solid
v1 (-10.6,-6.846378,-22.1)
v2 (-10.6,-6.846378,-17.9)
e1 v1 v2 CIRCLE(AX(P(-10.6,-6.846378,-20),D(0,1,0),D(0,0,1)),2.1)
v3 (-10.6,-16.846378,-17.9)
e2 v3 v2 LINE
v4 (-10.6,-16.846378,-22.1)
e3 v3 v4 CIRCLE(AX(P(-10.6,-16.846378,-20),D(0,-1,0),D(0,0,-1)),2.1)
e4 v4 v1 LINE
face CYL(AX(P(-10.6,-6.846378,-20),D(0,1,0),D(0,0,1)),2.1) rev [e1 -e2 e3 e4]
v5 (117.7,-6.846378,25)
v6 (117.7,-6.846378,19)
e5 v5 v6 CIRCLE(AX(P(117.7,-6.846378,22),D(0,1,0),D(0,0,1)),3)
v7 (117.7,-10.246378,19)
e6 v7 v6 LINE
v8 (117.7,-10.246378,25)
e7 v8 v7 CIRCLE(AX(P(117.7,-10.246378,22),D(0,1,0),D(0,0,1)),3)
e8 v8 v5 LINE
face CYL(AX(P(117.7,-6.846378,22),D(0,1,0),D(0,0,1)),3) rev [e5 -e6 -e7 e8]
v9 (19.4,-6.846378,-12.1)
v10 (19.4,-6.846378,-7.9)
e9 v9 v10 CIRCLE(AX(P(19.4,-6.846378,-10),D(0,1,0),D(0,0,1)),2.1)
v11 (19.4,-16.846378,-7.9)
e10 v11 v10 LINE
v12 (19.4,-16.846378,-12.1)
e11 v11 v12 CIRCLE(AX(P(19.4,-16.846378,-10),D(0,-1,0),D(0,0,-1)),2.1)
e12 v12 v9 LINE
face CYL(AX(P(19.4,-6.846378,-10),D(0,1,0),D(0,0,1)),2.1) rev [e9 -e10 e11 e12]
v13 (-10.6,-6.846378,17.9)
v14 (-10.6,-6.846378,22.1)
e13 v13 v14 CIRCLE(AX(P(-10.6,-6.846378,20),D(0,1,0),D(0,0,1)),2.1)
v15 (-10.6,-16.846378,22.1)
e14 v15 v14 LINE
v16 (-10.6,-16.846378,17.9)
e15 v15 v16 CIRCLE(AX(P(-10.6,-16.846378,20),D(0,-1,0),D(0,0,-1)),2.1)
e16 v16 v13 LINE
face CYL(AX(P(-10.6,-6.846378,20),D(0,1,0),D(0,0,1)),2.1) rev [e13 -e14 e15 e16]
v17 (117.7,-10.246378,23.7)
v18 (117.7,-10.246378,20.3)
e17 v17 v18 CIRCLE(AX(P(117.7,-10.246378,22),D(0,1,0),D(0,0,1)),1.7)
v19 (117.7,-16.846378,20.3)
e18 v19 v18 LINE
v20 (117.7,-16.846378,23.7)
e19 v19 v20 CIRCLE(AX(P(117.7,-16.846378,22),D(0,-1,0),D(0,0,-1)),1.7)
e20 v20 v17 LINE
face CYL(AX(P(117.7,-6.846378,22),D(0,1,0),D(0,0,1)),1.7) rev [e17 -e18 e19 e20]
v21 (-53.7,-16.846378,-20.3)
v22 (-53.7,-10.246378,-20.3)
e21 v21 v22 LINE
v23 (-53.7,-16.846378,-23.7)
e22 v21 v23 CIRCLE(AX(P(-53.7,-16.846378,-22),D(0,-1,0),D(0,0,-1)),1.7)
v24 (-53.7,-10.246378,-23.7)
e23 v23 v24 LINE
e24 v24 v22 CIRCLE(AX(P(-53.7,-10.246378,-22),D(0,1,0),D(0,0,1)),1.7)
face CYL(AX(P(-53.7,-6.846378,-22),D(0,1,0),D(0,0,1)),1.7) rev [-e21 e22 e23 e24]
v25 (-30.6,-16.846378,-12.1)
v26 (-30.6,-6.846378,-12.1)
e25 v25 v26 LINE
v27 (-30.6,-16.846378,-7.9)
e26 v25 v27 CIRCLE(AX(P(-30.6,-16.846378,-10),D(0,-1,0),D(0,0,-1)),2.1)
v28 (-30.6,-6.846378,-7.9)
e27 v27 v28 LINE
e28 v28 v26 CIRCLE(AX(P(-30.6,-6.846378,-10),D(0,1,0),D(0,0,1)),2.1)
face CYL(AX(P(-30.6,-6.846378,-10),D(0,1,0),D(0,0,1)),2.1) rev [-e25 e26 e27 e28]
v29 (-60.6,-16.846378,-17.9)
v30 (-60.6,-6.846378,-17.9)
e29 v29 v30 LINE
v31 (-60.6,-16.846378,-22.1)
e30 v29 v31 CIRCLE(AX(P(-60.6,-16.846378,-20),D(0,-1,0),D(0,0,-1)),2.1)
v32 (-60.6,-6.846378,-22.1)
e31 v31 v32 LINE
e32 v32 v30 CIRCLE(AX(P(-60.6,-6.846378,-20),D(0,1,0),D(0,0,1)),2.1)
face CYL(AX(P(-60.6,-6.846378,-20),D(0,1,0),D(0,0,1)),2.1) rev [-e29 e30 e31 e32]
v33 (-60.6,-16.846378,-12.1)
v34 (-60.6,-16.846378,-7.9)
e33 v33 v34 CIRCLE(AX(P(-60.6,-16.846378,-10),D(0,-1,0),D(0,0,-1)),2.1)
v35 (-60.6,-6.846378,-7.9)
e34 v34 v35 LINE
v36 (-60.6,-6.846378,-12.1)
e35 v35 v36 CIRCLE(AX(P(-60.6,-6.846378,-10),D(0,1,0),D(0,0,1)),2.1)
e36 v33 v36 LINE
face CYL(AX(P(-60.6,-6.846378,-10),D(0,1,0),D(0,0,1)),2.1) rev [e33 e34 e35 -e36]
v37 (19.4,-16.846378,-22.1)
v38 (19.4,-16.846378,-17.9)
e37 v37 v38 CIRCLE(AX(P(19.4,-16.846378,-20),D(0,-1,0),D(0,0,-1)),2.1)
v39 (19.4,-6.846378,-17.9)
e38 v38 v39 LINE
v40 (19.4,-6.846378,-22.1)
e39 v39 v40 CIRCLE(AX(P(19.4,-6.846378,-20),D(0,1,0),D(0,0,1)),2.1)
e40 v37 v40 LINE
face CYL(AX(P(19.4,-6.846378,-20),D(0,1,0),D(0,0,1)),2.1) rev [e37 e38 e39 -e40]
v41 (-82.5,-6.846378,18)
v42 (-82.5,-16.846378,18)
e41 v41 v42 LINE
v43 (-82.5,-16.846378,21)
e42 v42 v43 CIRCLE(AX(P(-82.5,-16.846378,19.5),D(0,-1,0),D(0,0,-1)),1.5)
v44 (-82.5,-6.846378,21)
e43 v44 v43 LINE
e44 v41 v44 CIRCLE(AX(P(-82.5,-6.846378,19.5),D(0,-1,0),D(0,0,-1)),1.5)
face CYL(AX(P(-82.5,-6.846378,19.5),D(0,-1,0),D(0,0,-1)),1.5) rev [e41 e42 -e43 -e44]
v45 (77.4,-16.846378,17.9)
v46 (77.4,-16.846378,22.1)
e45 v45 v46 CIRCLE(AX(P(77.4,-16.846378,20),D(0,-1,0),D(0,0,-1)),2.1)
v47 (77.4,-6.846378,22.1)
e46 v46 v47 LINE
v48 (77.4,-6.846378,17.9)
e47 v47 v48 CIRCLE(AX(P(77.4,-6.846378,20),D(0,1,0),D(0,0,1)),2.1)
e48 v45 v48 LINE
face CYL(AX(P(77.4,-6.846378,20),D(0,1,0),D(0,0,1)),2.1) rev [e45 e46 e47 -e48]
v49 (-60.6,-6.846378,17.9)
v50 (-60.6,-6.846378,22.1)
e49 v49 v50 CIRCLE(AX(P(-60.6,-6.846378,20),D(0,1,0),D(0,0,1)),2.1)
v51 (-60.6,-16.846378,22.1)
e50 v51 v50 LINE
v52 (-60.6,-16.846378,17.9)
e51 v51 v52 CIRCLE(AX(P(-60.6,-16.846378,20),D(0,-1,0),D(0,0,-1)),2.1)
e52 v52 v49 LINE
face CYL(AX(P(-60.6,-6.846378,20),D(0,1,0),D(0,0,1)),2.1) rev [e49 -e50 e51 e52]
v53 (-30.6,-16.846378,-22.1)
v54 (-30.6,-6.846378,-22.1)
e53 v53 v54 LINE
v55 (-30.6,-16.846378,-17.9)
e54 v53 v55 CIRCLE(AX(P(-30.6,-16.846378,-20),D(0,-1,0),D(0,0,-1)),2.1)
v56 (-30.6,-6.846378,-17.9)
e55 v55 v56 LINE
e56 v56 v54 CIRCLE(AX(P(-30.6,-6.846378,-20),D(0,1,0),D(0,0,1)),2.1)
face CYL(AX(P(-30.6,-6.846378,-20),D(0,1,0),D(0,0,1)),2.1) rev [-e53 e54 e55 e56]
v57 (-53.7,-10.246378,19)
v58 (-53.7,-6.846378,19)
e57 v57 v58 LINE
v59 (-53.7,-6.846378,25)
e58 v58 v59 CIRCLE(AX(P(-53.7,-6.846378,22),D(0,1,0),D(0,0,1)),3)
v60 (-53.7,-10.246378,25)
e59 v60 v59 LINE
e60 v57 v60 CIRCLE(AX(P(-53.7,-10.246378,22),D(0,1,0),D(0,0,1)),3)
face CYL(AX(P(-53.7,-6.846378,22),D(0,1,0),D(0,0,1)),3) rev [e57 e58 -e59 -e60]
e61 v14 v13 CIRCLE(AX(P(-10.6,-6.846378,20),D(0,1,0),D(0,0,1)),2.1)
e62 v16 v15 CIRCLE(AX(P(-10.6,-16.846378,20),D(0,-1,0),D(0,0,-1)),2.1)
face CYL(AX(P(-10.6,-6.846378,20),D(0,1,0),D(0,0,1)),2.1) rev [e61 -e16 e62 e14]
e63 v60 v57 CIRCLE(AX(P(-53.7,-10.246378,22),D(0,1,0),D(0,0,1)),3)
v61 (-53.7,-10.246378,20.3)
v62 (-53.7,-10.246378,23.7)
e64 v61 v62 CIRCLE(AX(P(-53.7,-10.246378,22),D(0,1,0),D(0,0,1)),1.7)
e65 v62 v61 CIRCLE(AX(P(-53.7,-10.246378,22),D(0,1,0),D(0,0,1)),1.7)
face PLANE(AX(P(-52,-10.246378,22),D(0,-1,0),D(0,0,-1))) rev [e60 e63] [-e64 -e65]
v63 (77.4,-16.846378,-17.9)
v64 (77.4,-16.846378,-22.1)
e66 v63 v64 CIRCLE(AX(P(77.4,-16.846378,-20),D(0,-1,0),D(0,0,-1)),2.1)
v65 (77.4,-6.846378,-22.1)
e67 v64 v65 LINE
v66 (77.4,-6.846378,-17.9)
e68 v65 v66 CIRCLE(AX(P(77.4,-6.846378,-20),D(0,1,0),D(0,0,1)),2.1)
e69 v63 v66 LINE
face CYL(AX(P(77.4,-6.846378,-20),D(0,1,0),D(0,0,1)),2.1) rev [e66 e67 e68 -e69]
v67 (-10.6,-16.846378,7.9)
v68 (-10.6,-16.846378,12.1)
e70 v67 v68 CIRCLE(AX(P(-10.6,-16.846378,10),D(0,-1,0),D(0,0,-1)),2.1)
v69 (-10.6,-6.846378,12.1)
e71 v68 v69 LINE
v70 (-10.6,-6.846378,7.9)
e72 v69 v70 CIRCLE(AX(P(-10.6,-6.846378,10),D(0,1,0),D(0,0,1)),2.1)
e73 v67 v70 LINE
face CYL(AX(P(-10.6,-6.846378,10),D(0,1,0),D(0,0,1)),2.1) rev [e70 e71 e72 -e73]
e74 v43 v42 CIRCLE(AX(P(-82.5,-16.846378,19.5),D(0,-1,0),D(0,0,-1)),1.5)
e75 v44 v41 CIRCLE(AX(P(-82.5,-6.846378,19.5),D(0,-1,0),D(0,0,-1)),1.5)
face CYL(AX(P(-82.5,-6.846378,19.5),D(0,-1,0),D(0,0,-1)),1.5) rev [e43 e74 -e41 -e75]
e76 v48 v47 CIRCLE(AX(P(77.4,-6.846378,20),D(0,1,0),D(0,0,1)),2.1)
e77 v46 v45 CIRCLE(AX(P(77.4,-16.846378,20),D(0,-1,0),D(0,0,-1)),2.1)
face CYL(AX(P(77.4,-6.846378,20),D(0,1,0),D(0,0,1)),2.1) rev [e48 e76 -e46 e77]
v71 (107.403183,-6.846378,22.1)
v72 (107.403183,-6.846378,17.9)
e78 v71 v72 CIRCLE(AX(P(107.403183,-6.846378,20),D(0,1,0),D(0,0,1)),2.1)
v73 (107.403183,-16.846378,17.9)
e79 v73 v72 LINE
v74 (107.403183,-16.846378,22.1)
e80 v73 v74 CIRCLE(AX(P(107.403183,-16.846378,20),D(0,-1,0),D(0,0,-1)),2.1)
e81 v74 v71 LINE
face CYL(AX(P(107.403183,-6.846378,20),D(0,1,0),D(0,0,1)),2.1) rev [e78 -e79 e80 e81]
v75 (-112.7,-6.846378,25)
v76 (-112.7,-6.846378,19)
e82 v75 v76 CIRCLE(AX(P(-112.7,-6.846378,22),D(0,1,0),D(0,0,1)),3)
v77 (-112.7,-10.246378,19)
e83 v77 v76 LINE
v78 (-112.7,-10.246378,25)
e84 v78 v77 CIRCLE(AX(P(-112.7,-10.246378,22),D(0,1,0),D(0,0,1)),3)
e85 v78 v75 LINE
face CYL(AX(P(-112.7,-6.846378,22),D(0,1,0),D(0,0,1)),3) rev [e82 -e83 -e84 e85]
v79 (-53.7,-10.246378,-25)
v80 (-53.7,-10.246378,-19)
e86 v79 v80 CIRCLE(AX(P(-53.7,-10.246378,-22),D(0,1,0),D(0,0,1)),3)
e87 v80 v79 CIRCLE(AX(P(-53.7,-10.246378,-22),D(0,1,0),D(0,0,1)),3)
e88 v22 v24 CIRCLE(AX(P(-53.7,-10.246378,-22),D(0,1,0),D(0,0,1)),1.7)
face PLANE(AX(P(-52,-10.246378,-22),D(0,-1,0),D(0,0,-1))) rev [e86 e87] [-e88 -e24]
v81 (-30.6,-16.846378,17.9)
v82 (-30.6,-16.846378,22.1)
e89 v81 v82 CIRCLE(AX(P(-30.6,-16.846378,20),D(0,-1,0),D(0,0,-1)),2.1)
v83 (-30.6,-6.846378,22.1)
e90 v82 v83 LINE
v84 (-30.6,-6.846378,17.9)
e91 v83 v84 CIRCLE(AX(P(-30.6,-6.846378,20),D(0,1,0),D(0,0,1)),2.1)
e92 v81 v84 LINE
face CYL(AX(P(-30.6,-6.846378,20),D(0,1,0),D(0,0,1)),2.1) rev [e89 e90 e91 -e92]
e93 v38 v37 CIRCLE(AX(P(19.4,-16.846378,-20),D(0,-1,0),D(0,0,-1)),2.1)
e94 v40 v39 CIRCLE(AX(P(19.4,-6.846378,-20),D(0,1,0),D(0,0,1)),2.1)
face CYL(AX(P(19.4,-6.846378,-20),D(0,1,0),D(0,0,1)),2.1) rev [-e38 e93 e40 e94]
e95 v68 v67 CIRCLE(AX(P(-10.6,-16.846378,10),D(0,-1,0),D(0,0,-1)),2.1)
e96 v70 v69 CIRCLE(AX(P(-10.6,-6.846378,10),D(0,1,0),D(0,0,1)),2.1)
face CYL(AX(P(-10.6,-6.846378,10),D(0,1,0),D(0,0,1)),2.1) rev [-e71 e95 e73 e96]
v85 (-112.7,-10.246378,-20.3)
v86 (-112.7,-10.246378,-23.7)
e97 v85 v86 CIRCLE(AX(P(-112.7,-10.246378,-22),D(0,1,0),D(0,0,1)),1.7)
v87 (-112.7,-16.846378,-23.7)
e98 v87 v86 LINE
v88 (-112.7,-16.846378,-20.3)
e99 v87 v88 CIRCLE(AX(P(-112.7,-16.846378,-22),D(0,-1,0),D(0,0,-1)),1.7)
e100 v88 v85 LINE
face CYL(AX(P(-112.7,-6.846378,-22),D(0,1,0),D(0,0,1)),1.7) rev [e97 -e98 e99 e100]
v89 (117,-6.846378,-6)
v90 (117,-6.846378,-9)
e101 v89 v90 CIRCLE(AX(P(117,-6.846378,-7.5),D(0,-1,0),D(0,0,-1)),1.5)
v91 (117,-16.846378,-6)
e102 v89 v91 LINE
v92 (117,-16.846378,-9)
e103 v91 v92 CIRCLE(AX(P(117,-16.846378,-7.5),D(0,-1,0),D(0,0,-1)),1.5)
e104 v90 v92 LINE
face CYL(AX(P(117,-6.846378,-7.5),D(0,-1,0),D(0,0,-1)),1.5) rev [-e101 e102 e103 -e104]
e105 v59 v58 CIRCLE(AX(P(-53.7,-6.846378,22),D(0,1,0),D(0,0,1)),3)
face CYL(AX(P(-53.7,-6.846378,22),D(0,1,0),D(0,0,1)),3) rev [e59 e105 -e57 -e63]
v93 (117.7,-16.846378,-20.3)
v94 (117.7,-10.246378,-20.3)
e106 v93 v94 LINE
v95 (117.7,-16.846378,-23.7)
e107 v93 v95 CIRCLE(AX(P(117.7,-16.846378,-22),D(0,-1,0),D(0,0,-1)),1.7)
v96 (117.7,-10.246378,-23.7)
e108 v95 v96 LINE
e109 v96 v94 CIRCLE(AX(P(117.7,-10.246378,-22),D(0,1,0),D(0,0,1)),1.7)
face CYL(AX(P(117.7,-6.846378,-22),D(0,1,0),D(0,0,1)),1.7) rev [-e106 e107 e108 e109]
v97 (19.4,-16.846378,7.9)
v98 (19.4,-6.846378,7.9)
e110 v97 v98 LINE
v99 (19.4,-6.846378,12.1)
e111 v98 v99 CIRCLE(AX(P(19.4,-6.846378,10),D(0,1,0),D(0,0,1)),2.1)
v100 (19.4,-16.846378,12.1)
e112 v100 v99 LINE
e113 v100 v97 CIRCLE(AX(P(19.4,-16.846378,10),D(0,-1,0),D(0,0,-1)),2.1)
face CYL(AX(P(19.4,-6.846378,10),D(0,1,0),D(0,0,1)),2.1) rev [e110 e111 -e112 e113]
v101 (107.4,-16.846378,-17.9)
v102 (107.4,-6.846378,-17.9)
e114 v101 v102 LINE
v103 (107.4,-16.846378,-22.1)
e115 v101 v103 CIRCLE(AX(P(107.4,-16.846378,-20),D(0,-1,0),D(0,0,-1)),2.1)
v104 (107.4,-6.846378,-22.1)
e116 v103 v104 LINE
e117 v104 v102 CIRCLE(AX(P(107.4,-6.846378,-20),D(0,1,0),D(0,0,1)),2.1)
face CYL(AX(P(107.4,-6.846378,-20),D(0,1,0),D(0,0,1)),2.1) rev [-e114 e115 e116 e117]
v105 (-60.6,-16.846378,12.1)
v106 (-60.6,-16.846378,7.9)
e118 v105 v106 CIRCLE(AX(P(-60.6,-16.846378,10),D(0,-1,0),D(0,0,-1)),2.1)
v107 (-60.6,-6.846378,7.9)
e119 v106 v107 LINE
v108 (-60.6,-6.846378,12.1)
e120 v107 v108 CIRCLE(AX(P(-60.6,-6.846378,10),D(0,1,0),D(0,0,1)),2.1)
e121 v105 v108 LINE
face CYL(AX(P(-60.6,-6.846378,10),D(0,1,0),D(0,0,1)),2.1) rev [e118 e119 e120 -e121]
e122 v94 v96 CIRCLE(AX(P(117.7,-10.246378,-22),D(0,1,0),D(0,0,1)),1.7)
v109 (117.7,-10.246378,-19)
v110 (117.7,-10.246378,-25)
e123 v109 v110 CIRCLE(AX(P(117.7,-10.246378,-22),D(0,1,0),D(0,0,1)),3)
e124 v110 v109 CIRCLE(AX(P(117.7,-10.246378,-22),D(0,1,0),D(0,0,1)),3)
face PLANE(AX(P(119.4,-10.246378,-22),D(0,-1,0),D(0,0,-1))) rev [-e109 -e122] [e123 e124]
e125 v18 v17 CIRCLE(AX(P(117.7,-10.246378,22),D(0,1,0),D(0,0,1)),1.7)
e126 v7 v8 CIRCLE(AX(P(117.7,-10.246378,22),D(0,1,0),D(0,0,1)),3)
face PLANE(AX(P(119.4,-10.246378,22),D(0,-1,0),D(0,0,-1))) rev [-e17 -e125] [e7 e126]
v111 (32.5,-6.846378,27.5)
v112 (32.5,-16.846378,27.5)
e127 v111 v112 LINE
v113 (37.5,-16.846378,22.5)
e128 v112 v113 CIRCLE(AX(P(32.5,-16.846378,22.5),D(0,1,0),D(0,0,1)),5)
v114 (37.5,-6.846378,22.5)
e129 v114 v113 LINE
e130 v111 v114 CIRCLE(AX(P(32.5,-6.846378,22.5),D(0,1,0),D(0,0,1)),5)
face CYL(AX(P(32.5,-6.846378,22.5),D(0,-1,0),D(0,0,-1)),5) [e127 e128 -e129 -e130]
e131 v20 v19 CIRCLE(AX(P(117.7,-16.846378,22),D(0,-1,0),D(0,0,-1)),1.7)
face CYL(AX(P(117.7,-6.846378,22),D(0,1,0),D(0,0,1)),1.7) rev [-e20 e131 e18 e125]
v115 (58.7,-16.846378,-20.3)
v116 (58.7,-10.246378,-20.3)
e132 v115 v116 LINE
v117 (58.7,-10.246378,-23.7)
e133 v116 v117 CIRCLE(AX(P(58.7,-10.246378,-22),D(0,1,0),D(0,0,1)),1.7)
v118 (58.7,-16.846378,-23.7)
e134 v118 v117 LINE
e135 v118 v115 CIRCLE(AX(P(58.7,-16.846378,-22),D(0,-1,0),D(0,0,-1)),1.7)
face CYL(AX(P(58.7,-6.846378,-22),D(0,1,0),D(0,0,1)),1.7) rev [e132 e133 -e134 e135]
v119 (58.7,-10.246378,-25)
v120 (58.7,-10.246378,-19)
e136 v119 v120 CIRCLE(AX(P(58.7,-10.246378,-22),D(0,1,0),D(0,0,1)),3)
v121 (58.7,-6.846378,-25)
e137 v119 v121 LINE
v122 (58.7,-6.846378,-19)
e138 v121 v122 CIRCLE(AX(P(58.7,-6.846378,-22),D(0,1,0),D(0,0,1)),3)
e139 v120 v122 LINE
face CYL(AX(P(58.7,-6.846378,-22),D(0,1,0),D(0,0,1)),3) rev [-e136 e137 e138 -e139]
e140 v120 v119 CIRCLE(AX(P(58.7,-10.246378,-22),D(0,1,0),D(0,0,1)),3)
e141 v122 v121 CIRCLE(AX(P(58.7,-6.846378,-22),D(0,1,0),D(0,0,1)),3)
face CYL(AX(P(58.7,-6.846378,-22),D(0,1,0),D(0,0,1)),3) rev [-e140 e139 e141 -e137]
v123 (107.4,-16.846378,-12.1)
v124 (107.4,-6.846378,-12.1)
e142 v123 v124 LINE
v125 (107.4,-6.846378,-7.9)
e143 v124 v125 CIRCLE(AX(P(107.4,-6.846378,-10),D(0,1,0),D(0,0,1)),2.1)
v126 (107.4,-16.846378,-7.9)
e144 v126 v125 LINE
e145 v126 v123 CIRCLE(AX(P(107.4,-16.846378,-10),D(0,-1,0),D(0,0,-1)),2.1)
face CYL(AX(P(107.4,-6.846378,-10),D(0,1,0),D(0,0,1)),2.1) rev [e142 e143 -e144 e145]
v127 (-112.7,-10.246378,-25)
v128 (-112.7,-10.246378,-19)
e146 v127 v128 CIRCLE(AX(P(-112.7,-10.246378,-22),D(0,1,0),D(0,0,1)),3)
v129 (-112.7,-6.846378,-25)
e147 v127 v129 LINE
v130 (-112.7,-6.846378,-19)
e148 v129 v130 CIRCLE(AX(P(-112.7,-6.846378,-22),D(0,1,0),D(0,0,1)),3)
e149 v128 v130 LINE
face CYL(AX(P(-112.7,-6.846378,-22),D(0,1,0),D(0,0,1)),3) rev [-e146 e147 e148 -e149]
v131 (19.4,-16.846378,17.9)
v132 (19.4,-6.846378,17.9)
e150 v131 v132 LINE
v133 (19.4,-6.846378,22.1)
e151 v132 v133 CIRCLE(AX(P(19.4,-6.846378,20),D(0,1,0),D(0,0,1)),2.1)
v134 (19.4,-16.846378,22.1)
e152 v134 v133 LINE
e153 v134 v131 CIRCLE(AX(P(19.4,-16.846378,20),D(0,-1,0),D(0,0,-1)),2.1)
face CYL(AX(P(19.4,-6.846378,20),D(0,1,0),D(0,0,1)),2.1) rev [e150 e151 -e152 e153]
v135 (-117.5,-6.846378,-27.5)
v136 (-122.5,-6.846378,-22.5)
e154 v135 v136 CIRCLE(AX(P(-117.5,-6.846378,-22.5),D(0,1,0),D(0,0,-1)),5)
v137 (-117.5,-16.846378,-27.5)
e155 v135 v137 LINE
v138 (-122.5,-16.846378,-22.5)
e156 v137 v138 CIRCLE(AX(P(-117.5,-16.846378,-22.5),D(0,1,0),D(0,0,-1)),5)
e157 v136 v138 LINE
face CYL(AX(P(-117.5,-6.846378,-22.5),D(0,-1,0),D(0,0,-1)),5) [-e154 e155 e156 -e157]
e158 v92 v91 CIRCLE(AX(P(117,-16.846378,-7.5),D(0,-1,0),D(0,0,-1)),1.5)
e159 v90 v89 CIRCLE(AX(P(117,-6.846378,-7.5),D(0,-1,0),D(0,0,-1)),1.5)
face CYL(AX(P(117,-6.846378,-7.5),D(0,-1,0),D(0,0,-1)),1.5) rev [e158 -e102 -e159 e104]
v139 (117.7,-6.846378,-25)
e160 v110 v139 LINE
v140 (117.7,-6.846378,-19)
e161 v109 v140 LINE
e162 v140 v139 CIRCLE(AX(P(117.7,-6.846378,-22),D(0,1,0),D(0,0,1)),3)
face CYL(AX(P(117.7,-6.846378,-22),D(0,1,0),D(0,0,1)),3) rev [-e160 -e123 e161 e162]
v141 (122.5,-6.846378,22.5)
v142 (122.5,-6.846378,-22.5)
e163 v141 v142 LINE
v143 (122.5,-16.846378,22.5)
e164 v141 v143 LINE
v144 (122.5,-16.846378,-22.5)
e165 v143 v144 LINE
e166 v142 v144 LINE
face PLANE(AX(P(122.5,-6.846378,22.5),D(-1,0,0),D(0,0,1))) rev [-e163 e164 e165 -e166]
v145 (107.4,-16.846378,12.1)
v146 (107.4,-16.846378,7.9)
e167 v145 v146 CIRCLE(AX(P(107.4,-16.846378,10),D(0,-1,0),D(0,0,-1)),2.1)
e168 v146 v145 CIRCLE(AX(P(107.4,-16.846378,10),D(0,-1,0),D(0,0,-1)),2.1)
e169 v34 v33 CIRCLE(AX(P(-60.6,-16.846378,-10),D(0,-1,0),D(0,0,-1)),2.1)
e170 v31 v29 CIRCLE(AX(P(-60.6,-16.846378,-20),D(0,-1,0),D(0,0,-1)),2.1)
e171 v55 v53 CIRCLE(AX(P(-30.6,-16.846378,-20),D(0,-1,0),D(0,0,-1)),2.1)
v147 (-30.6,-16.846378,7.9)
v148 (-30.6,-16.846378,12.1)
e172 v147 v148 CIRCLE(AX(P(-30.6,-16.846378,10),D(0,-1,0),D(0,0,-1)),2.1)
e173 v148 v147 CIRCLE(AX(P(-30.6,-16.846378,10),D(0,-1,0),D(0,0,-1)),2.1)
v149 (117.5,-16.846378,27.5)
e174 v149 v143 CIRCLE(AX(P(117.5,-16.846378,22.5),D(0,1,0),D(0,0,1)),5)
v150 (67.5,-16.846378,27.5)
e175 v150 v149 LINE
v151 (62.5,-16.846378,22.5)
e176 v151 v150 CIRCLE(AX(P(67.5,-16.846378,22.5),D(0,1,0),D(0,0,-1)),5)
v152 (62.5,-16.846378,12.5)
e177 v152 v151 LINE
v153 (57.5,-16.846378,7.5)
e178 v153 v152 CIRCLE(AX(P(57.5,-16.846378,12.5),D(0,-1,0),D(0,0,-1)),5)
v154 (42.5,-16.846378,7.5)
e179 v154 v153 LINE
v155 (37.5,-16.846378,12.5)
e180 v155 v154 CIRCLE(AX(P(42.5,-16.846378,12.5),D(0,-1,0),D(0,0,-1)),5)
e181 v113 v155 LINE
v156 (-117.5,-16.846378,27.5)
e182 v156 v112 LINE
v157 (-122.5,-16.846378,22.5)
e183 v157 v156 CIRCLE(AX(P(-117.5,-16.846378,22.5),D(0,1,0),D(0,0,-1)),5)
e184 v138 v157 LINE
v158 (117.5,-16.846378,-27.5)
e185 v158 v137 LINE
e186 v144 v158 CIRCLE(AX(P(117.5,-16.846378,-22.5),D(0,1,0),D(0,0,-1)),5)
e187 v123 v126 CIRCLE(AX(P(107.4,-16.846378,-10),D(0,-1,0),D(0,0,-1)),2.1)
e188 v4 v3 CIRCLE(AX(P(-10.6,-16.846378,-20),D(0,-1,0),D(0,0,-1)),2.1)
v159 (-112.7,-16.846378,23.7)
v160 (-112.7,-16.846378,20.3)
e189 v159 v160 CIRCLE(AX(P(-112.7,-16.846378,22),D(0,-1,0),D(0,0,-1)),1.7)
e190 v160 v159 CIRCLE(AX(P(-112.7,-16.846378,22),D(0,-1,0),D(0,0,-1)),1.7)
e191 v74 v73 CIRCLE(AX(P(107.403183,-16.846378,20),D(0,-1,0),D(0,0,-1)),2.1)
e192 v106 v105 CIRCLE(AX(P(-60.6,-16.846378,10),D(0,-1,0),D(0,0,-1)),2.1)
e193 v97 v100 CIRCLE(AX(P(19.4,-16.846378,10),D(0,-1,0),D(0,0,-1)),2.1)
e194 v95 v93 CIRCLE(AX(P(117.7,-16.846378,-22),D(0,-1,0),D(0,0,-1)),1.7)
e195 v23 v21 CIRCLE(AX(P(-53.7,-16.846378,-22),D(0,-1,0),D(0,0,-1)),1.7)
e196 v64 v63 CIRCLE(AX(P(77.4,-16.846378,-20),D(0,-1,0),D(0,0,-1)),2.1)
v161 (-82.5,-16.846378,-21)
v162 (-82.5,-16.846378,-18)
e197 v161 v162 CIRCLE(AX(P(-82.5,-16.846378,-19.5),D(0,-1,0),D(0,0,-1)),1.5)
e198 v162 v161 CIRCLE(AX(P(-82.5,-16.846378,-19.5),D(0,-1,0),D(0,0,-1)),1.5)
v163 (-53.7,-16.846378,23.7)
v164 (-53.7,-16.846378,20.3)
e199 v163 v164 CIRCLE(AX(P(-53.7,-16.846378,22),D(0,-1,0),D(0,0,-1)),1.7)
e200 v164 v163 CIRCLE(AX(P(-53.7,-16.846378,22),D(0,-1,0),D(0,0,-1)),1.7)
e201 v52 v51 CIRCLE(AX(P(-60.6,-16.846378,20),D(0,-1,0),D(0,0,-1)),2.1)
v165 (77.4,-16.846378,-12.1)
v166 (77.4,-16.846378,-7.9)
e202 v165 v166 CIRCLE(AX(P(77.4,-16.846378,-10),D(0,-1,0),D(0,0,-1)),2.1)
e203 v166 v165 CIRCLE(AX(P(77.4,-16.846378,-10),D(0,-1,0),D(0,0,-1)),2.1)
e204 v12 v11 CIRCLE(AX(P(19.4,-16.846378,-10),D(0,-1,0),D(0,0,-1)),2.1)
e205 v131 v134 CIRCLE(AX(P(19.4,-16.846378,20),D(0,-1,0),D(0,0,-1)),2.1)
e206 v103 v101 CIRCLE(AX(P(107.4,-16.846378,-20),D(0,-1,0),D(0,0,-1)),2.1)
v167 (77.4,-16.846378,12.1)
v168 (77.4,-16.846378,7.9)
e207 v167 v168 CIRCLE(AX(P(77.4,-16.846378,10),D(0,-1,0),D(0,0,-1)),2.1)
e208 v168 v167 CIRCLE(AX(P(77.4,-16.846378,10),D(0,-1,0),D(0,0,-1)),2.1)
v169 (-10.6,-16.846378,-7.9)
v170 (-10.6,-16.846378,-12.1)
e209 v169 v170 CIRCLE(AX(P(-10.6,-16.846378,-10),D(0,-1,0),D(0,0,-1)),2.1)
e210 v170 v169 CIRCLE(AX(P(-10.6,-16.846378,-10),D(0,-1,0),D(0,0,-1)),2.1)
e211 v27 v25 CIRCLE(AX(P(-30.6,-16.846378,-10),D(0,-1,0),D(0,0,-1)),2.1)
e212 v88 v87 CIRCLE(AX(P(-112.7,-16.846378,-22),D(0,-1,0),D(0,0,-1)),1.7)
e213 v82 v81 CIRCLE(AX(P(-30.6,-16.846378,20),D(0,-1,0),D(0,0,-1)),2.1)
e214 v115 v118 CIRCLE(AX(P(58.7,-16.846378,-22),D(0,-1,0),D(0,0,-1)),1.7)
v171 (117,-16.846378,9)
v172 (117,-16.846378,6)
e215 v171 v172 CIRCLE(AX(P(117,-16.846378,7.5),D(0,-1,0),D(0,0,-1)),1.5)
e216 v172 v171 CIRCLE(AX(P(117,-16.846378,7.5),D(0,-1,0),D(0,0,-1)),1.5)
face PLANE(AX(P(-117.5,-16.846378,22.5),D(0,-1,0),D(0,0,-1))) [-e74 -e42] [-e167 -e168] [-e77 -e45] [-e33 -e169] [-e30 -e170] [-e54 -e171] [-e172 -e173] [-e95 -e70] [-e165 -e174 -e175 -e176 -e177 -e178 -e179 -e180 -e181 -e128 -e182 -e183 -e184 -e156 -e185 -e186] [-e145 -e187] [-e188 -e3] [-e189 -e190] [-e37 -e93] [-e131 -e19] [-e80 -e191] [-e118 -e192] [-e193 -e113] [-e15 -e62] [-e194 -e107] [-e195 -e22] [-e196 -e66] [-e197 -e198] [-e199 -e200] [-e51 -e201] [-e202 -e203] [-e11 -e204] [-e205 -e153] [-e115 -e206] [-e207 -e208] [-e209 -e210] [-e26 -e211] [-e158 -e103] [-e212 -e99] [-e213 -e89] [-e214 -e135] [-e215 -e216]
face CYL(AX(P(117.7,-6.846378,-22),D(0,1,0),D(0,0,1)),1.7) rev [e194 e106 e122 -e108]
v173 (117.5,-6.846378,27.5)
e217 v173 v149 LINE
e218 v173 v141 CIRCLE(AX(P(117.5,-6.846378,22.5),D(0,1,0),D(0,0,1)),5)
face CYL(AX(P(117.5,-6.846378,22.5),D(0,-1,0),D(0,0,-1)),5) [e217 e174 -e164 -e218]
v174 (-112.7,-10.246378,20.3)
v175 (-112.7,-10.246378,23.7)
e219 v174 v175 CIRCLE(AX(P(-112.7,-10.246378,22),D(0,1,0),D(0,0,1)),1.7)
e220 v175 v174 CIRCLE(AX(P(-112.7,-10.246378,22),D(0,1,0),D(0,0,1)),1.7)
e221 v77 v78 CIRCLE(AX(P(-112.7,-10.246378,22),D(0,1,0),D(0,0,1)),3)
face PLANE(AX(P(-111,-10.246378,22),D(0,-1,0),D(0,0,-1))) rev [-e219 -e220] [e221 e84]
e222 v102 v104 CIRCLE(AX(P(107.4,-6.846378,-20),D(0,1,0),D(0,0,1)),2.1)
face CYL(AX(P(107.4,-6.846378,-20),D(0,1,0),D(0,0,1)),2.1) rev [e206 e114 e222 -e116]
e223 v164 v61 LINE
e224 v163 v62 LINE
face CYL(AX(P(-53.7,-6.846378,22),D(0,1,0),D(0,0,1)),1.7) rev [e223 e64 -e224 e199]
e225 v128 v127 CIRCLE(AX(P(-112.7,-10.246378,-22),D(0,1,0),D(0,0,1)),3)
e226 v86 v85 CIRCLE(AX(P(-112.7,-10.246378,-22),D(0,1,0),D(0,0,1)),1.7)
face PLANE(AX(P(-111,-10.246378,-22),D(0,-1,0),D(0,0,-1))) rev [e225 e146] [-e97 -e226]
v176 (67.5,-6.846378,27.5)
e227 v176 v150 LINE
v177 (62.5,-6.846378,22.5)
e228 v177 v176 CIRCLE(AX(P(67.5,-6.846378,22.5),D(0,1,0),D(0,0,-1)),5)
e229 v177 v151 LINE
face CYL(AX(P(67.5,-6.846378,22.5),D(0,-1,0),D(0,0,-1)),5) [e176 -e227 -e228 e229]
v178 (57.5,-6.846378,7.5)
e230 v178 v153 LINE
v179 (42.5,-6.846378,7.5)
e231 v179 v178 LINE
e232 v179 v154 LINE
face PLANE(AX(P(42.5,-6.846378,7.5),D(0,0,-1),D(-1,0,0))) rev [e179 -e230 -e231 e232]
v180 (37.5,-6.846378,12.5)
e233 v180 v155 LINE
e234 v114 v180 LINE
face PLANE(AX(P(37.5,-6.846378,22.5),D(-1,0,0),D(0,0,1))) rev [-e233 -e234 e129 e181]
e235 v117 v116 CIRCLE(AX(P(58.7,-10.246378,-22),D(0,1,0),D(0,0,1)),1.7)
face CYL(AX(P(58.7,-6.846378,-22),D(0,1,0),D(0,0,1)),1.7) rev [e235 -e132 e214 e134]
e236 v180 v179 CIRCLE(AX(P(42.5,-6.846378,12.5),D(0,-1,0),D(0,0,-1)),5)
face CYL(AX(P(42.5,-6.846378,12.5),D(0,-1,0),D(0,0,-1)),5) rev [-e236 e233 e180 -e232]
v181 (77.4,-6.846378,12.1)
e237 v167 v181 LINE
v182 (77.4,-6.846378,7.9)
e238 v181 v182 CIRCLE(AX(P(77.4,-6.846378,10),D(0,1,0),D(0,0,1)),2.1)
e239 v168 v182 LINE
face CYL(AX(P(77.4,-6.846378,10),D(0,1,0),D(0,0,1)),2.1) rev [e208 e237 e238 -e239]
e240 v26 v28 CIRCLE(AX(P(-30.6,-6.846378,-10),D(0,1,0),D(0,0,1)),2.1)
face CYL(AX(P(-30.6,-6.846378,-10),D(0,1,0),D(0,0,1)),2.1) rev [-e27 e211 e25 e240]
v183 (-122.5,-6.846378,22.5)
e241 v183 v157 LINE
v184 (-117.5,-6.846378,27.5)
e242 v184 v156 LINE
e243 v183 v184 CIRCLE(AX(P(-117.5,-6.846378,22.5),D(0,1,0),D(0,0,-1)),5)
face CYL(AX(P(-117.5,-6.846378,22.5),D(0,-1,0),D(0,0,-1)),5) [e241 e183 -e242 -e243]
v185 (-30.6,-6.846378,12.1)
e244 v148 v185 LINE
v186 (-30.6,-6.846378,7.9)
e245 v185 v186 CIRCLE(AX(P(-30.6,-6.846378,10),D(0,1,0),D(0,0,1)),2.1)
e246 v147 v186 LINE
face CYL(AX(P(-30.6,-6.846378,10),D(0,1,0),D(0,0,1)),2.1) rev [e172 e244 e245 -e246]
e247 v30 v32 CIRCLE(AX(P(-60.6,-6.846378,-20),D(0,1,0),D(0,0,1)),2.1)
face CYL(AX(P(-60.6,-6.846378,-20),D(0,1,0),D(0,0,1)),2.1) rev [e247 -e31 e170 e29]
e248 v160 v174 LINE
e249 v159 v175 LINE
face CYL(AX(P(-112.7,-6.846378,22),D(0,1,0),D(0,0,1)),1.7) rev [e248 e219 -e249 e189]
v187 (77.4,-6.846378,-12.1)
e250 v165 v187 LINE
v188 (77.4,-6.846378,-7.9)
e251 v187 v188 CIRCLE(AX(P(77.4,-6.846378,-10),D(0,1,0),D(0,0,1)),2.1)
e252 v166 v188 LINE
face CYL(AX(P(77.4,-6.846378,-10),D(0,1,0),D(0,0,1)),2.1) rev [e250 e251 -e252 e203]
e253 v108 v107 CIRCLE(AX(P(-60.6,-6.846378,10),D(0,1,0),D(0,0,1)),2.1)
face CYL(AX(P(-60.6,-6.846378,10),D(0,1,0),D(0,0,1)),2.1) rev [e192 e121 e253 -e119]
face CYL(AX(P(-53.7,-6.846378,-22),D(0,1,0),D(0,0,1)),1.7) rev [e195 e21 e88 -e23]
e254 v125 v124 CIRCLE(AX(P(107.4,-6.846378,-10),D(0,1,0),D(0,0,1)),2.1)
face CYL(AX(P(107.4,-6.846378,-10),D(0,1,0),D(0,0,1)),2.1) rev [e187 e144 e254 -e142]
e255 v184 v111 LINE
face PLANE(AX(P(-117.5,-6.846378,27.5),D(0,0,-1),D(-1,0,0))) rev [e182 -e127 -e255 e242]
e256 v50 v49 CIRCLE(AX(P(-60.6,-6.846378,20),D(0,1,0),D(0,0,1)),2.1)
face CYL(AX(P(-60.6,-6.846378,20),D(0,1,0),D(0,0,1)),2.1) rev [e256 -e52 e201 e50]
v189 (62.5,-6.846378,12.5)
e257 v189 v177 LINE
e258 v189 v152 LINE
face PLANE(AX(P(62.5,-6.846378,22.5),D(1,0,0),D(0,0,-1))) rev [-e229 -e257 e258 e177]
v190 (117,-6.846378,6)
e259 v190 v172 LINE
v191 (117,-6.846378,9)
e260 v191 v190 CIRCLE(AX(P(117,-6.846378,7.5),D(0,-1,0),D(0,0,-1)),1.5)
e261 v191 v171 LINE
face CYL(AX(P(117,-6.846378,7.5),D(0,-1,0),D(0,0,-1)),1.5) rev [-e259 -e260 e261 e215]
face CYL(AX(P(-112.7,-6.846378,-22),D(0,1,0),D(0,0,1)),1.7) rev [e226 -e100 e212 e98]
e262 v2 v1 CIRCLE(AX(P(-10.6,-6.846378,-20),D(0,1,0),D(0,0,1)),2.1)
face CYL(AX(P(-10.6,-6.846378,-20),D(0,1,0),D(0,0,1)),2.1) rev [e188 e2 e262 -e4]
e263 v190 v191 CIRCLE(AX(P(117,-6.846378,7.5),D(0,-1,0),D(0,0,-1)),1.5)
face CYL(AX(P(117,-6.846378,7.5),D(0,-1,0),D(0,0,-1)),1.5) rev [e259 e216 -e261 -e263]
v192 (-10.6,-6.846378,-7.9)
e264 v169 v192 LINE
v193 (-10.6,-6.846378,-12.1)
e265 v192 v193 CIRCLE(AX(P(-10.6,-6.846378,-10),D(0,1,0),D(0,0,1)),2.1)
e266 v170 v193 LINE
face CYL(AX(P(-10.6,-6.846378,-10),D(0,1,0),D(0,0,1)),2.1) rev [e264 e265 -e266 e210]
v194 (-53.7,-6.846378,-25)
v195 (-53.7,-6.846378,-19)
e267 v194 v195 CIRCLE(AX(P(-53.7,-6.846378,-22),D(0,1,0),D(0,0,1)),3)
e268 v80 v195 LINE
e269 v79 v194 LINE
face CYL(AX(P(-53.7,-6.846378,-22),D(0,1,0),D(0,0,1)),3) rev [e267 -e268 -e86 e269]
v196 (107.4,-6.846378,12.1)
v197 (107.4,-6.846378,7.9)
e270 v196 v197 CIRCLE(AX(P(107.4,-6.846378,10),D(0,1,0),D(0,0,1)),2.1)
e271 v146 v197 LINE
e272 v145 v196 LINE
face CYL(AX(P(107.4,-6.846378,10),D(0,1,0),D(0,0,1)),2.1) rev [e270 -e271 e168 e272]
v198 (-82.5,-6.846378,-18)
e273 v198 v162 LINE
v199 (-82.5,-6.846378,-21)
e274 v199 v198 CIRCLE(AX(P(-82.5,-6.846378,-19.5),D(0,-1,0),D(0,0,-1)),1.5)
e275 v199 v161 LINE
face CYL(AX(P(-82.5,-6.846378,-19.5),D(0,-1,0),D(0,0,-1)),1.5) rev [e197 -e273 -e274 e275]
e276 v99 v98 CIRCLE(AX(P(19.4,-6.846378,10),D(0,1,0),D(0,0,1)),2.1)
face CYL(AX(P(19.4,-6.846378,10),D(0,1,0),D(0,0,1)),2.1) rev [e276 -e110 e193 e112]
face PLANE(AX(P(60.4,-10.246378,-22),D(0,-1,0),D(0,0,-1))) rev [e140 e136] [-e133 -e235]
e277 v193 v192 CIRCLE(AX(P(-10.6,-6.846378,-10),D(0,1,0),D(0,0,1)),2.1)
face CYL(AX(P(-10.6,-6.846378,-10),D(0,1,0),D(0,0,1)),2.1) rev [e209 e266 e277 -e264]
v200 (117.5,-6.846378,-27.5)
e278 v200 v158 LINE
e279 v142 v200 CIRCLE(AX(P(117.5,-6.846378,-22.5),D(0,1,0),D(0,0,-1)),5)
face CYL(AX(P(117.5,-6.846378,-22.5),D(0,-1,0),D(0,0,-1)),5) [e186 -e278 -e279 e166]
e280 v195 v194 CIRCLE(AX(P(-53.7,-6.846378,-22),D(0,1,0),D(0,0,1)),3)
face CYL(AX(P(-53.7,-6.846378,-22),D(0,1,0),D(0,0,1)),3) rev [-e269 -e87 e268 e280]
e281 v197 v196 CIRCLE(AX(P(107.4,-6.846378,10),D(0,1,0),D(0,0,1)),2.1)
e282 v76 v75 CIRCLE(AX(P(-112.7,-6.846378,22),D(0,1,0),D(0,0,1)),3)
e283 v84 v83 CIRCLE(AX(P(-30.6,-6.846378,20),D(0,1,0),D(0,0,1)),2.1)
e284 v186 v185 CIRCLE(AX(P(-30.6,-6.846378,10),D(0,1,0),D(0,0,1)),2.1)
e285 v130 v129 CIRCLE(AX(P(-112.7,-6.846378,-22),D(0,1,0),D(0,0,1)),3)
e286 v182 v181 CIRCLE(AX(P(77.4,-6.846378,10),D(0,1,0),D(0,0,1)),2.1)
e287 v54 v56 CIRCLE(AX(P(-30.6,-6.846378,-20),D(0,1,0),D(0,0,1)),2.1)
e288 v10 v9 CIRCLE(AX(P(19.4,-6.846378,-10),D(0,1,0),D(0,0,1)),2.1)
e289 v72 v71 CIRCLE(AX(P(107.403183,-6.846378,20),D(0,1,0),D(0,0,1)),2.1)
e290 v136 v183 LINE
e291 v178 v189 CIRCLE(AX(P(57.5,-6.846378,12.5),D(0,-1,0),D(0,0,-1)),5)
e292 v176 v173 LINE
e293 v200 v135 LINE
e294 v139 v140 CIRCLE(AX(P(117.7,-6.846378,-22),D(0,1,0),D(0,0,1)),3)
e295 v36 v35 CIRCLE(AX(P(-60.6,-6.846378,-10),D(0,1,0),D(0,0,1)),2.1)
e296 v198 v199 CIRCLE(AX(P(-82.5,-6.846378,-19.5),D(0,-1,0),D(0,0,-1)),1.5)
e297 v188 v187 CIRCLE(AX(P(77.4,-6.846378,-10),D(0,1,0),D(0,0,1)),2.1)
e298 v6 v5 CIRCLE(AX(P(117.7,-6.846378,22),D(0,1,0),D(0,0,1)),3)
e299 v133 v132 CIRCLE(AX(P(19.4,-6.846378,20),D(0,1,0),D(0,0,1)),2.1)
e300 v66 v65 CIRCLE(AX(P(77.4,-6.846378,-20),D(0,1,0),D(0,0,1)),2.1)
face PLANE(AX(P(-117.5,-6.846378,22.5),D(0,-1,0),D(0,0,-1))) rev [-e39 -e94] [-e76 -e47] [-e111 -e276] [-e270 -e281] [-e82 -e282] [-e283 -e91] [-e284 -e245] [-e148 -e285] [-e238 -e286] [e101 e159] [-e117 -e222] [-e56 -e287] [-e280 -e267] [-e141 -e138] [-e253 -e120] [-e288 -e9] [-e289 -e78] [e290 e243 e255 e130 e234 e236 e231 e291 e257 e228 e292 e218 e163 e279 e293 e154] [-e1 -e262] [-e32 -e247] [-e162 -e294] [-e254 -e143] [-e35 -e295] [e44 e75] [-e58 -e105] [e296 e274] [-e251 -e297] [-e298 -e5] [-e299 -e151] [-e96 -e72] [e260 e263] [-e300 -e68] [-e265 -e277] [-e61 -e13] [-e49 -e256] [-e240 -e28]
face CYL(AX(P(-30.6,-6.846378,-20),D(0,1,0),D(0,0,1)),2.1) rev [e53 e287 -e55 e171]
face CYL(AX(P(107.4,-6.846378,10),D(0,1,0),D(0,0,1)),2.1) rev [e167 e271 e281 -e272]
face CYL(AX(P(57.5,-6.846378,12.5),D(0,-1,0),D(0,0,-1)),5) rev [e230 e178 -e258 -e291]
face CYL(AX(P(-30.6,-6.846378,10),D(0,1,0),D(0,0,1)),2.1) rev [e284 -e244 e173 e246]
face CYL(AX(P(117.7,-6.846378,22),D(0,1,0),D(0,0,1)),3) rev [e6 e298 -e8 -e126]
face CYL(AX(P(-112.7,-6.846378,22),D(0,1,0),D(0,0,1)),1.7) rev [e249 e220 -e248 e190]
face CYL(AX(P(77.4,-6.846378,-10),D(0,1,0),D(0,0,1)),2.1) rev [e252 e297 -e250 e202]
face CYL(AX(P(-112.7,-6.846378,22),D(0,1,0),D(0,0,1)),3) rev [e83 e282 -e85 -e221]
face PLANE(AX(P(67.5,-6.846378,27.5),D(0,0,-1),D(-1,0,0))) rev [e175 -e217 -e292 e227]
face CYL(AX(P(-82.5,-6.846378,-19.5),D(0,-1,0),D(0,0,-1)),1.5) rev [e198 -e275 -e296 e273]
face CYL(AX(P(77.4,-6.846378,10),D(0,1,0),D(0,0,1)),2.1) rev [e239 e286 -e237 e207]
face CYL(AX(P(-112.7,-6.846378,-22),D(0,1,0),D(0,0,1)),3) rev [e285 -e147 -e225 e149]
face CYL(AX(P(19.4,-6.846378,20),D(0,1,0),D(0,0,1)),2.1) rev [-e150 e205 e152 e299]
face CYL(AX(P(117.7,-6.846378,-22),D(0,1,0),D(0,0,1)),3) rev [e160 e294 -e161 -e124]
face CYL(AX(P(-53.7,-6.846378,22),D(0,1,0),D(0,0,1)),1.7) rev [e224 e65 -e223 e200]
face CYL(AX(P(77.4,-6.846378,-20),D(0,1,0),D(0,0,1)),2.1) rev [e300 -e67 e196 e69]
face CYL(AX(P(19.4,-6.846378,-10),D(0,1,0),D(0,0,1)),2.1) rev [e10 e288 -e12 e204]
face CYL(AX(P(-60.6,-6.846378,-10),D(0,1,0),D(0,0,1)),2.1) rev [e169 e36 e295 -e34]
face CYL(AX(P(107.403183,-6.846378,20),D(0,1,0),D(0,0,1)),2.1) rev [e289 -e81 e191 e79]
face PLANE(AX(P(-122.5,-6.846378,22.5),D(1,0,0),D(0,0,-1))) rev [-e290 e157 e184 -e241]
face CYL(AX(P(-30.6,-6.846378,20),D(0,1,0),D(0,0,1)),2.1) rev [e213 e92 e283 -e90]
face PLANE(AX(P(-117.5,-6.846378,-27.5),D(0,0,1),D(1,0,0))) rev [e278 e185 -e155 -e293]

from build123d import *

# Parameters (mm, degrees)
BOSS_EXTRUDE1_DEPTH                                  = 10
CBORE_FOR_M3_HEXAGON_SOCKET_HEAD_CAP_SCR_D           = 3.4
CBORE_FOR_M3_HEXAGON_SOCKET_HEAD_CAP_SCR_DEPTH       = 17
CBORE_FOR_M3_HEXAGON_SOCKET_HEAD_CAP_SCR_CBORE_D     = 6
CBORE_FOR_M3_HEXAGON_SOCKET_HEAD_CAP_SCR_CBORE_DEPTH = 3.4
CBORE_FOR_M3_HEXAGON_SOCKET_HEAD_CAP_SCR_TIP         = 1.021463052
M5_TAPPED_HOLE1_AT_2_COUNT                           = 2
M5_TAPPED_HOLE1_AT_2_PITCH                           = 30
M5_TAPPED_HOLE1_AT_3_COUNT                           = 2
M5_TAPPED_HOLE1_AT_3_PITCH                           = 42.426406871
M5_TAPPED_HOLE1_AT_4_COUNT                           = 2
M5_TAPPED_HOLE1_AT_4_PITCH                           = 10
M5_TAPPED_HOLE1_AT_5_COUNT                           = 2
M5_TAPPED_HOLE1_AT_5_PITCH                           = 31.622776602
M5_TAPPED_HOLE1_AT_6_COUNT                           = 2
M5_TAPPED_HOLE1_AT_6_PITCH                           = 141.223227551
M5_TAPPED_HOLE1_AT_7_COUNT                           = 2
M5_TAPPED_HOLE1_AT_7_PITCH                           = 170.65755184
M5_TAPPED_HOLE1_AT_8_COUNT                           = 2
M5_TAPPED_HOLE1_AT_8_PITCH                           = 138.361844451
M5_TAPPED_HOLE1_AT_9_COUNT                           = 2
M5_TAPPED_HOLE1_AT_9_PITCH                           = 168.300533599
M5_TAPPED_HOLE1_AT_10_COUNT                          = 2
M5_TAPPED_HOLE1_AT_10_PITCH                          = 36.055512755
M5_TAPPED_HOLE1_AT_11_COUNT                          = 2
M5_TAPPED_HOLE1_AT_11_PITCH                          = 20
M5_TAPPED_HOLE1_AT_12_COUNT                          = 2
M5_TAPPED_HOLE1_AT_12_PITCH                          = 139.441744108
M5_TAPPED_HOLE1_AT_13_COUNT                          = 2
M5_TAPPED_HOLE1_AT_13_PITCH                          = 169.18628786
M5_TAPPED_HOLE1_AT_14_COUNT                          = 2
M5_TAPPED_HOLE1_AT_14_PITCH                          = 168
M5_TAPPED_HOLE1_AT_15_COUNT                          = 2
M5_TAPPED_HOLE1_AT_15_PITCH                          = 138
M5_TAPPED_HOLE1_AT_16_COUNT                          = 2
M5_TAPPED_HOLE1_AT_16_PITCH                          = 30
SKETCH6_R                                            = 1.5
CUT_EXTRUDE1_DEPTH                                   = 126.946417178
LPATTERN1_COUNT                                      = 2
LPATTERN1_PITCH                                      = 50


with BuildPart() as part:
    # Sketch1 → Boss-Extrude1 (new body)
    with BuildSketch(Plane(origin=(0, -16.846378111, 0), x_dir=(1, 0, 0), z_dir=(0, 1, 0))):
        with BuildLine():
            Line((67.5, -27.5), (117.5, -27.5))
            ThreePointArc((117.5, -27.5), (121.035533906, -26.035533906), (122.5, -22.5))
            Line((122.5, -22.5), (122.5, 22.5))
            ThreePointArc((122.5, 22.5), (121.035533906, 26.035533906), (117.5, 27.5))
            Line((117.5, 27.5), (-117.5, 27.5))
            ThreePointArc((-117.5, 27.5), (-121.035533906, 26.035533906), (-122.5, 22.5))
            Line((-122.5, 22.5), (-122.5, -22.5))
            ThreePointArc((-122.5, -22.5), (-121.035533906, -26.035533906), (-117.5, -27.5))
            Line((-117.5, -27.5), (32.5, -27.5))
            ThreePointArc((32.5, -27.5), (36.035533906, -26.035533906), (37.5, -22.5))
            Line((37.5, -22.5), (37.5, -12.5))
            ThreePointArc((37.5, -12.5), (38.964466094, -8.964466094), (42.5, -7.5))
            Line((42.5, -7.5), (57.5, -7.5))
            ThreePointArc((57.5, -7.5), (61.035533906, -8.964466094), (62.5, -12.5))
            Line((62.5, -12.5), (62.5, -22.5))
            ThreePointArc((62.5, -22.5), (63.964466094, -26.035533906), (67.5, -27.5))
        make_face()
    extrude(amount=BOSS_EXTRUDE1_DEPTH)

    # CBORE for M3 Hexagon socket head cap screws1
    with Locations(Plane(origin=(0, -6.846378111, 0), x_dir=(1, 0, 0), z_dir=(0, 1, 0))):
        with Locations((117.7, 22), (58.7, 22), (117.7, -22), (-53.7, -22), (-53.7, 22), (-112.7, 22), (-112.7, -22)):
            CounterBoreHole(CBORE_FOR_M3_HEXAGON_SOCKET_HEAD_CAP_SCR_D / 2, CBORE_FOR_M3_HEXAGON_SOCKET_HEAD_CAP_SCR_CBORE_D / 2, CBORE_FOR_M3_HEXAGON_SOCKET_HEAD_CAP_SCR_CBORE_DEPTH, depth=CBORE_FOR_M3_HEXAGON_SOCKET_HEAD_CAP_SCR_DEPTH)
            with Locations((0, 0, -(CBORE_FOR_M3_HEXAGON_SOCKET_HEAD_CAP_SCR_DEPTH + CBORE_FOR_M3_HEXAGON_SOCKET_HEAD_CAP_SCR_TIP / 2))):  # 118° drill point
                Cone(0, CBORE_FOR_M3_HEXAGON_SOCKET_HEAD_CAP_SCR_D / 2, CBORE_FOR_M3_HEXAGON_SOCKET_HEAD_CAP_SCR_TIP, mode=Mode.SUBTRACT)

    # Sketch5 → M5 Tapped Hole1 (revolve, cut)
    with BuildSketch(Plane(origin=(-60.6, -6.846378111, 10), x_dir=(0, 0, 1), z_dir=(1, 0, 0))):
        Polygon((0, 0), (0, 15.2618073), (2.1, 14), (2.1, 0), align=None)
    m5_tapped_hole1 = revolve(axis=Axis((-60.6, -0.496378111, 10), (0, -1, 0)), mode=Mode.SUBTRACT)

    # M5 Tapped Hole1 at 2: M5 Tapped Hole1 ×2
    with Locations(*[(0, 0, -i * M5_TAPPED_HOLE1_AT_2_PITCH) for i in range(1, M5_TAPPED_HOLE1_AT_2_COUNT)]):
        add(m5_tapped_hole1, mode=Mode.SUBTRACT)

    # M5 Tapped Hole1 at 3: M5 Tapped Hole1 ×2
    with Locations(*[Vector(0.7071067811865475, 0, -0.7071067811865476) * (i * M5_TAPPED_HOLE1_AT_3_PITCH) for i in range(1, M5_TAPPED_HOLE1_AT_3_COUNT)]):
        add(m5_tapped_hole1, mode=Mode.SUBTRACT)

    # M5 Tapped Hole1 at 4: M5 Tapped Hole1 ×2
    with Locations(*[(0, 0, i * M5_TAPPED_HOLE1_AT_4_PITCH) for i in range(1, M5_TAPPED_HOLE1_AT_4_COUNT)]):
        add(m5_tapped_hole1, mode=Mode.SUBTRACT)

    # M5 Tapped Hole1 at 5: M5 Tapped Hole1 ×2
    with Locations(*[Vector(0.9486832980505138, 0, 0.3162277660168382) * (i * M5_TAPPED_HOLE1_AT_5_PITCH) for i in range(1, M5_TAPPED_HOLE1_AT_5_COUNT)]):
        add(m5_tapped_hole1, mode=Mode.SUBTRACT)

    # M5 Tapped Hole1 at 6: M5 Tapped Hole1 ×2
    with Locations(*[Vector(0.9771763639228009, 0, -0.21242964433104378) * (i * M5_TAPPED_HOLE1_AT_6_PITCH) for i in range(1, M5_TAPPED_HOLE1_AT_6_COUNT)]):
        add(m5_tapped_hole1, mode=Mode.SUBTRACT)

    # M5 Tapped Hole1 at 7: M5 Tapped Hole1 ×2
    with Locations(*[Vector(0.984427575508482, 0, -0.17579063848365759) * (i * M5_TAPPED_HOLE1_AT_7_PITCH) for i in range(1, M5_TAPPED_HOLE1_AT_7_COUNT)]):
        add(m5_tapped_hole1, mode=Mode.SUBTRACT)

    # M5 Tapped Hole1 at 8: M5 Tapped Hole1 ×2
    with Locations(*[Vector(0.9973847959828921, 0, 0.0722742605784705) * (i * M5_TAPPED_HOLE1_AT_8_PITCH) for i in range(1, M5_TAPPED_HOLE1_AT_8_COUNT)]):
        add(m5_tapped_hole1, mode=Mode.SUBTRACT)

    # M5 Tapped Hole1 at 9: M5 Tapped Hole1 ×2
    with Locations(*[Vector(0.9982332185134931, 0, 0.05941751809182934) * (i * M5_TAPPED_HOLE1_AT_9_PITCH) for i in range(1, M5_TAPPED_HOLE1_AT_9_COUNT)]):
        add(m5_tapped_hole1, mode=Mode.SUBTRACT)

    # M5 Tapped Hole1 at 10: M5 Tapped Hole1 ×2
    with Locations(*[Vector(0.8320502943378436, 0, -0.5547001962252293) * (i * M5_TAPPED_HOLE1_AT_10_PITCH) for i in range(1, M5_TAPPED_HOLE1_AT_10_COUNT)]):
        add(m5_tapped_hole1, mode=Mode.SUBTRACT)

    # M5 Tapped Hole1 at 11: M5 Tapped Hole1 ×2
    with Locations(*[(0, 0, -i * M5_TAPPED_HOLE1_AT_11_PITCH) for i in range(1, M5_TAPPED_HOLE1_AT_11_COUNT)]):
        add(m5_tapped_hole1, mode=Mode.SUBTRACT)

    # M5 Tapped Hole1 at 12: M5 Tapped Hole1 ×2
    with Locations(*[Vector(0.9896605990003554, 0, -0.14342907231889213) * (i * M5_TAPPED_HOLE1_AT_12_PITCH) for i in range(1, M5_TAPPED_HOLE1_AT_12_COUNT)]):
        add(m5_tapped_hole1, mode=Mode.SUBTRACT)

    # M5 Tapped Hole1 at 13: M5 Tapped Hole1 ×2
    with Locations(*[Vector(0.9929882741949438, 0, -0.11821288978511241) * (i * M5_TAPPED_HOLE1_AT_13_PITCH) for i in range(1, M5_TAPPED_HOLE1_AT_13_COUNT)]):
        add(m5_tapped_hole1, mode=Mode.SUBTRACT)

    # M5 Tapped Hole1 at 14: M5 Tapped Hole1 ×2
    with Locations(*[(i * M5_TAPPED_HOLE1_AT_14_PITCH, 0, 0) for i in range(1, M5_TAPPED_HOLE1_AT_14_COUNT)]):
        add(m5_tapped_hole1, mode=Mode.SUBTRACT)

    # M5 Tapped Hole1 at 15: M5 Tapped Hole1 ×2
    with Locations(*[(i * M5_TAPPED_HOLE1_AT_15_PITCH, 0, 0) for i in range(1, M5_TAPPED_HOLE1_AT_15_COUNT)]):
        add(m5_tapped_hole1, mode=Mode.SUBTRACT)

    # M5 Tapped Hole1 at 16: M5 Tapped Hole1 ×2
    with Locations(*[(i * M5_TAPPED_HOLE1_AT_16_PITCH, 0, 0) for i in range(1, M5_TAPPED_HOLE1_AT_16_COUNT)]):
        add(m5_tapped_hole1, mode=Mode.SUBTRACT)

    # Sketch6 → Cut-Extrude1 (cut, through all)
    with BuildSketch(Plane.XZ.offset(16.846378111)):
        with Locations(Location((-82.5, 19.5, 0), (0, 0, 270))):
            Circle(SKETCH6_R)
        with Locations(Location((-82.5, -19.5, 0), (0, 0, 270))):
            Circle(SKETCH6_R)
        with Locations(Location((117, 7.5, 0), (0, 0, 270))):
            Circle(SKETCH6_R)
        with Locations(Location((117, -7.5, 0), (0, 0, 270))):
            Circle(SKETCH6_R)
    extrude(amount=-CUT_EXTRUDE1_DEPTH, mode=Mode.SUBTRACT)

    # LPattern1: M5 Tapped Hole1 ×2
    with Locations(*[(i * LPATTERN1_PITCH, 0, 0) for i in range(1, LPATTERN1_COUNT)]):
        add(m5_tapped_hole1, mode=Mode.SUBTRACT)

    # LPattern1 copy 1 sketch → LPattern1 copy 1 (revolve, cut)
    with BuildSketch(Plane(origin=(-10.6, -6.846378111, -20), x_dir=(0, 0, 1), z_dir=(1, 0, 0))):
        Polygon((0, 0), (0, 15.2618073), (2.1, 14), (2.1, 0), align=None)
    revolve(axis=Axis((-10.6, -0.496378111, -20), (0, -1, 0)), mode=Mode.SUBTRACT)

    # LPattern1 copy 2 sketch → LPattern1 copy 2 (revolve, cut)
    with BuildSketch(Plane(origin=(19.4, -6.846378111, -20), x_dir=(0, 0, 1), z_dir=(1, 0, 0))):
        Polygon((0, 0), (0, 15.2618073), (2.1, 14), (2.1, 0), align=None)
    revolve(axis=Axis((19.4, -0.496378111, -20), (0, -1, 0)), mode=Mode.SUBTRACT)

    # LPattern1 copy 3 sketch → LPattern1 copy 3 (revolve, cut)
    with BuildSketch(Plane(origin=(-10.6, -6.846378111, 20), x_dir=(0, 0, 1), z_dir=(1, 0, 0))):
        Polygon((0, 0), (0, 15.2618073), (2.1, 14), (2.1, 0), align=None)
    revolve(axis=Axis((-10.6, -0.496378111, 20), (0, -1, 0)), mode=Mode.SUBTRACT)

    # LPattern1 copy 4 sketch → LPattern1 copy 4 (revolve, cut)
    with BuildSketch(Plane(origin=(19.4, -6.846378111, 20), x_dir=(0, 0, 1), z_dir=(1, 0, 0))):
        Polygon((0, 0), (0, 15.2618073), (2.1, 14), (2.1, 0), align=None)
    revolve(axis=Axis((19.4, -0.496378111, 20), (0, -1, 0)), mode=Mode.SUBTRACT)

    # LPattern1 copy 5 sketch → LPattern1 copy 5 (revolve, cut)
    with BuildSketch(Plane(origin=(127.4, -6.846378111, -20), x_dir=(0, 0, 1), z_dir=(1, 0, 0))):
        Polygon((0, 0), (0, 15.2618073), (2.1, 14), (2.1, 0), align=None)
    revolve(axis=Axis((127.4, -0.496378111, -20), (0, -1, 0)), mode=Mode.SUBTRACT)

    # LPattern1 copy 6 sketch → LPattern1 copy 6 (revolve, cut)
    with BuildSketch(Plane(origin=(157.4, -6.846378111, -20), x_dir=(0, 0, 1), z_dir=(1, 0, 0))):
        Polygon((0, 0), (0, 15.2618073), (2.1, 14), (2.1, 0), align=None)
    revolve(axis=Axis((157.4, -0.496378111, -20), (0, -1, 0)), mode=Mode.SUBTRACT)

    # LPattern1 copy 7 sketch → LPattern1 copy 7 (revolve, cut)
    with BuildSketch(Plane(origin=(127.4, -6.846378111, 20), x_dir=(0, 0, 1), z_dir=(1, 0, 0))):
        Polygon((0, 0), (0, 15.2618073), (2.1, 14), (2.1, 0), align=None)
    revolve(axis=Axis((127.4, -0.496378111, 20), (0, -1, 0)), mode=Mode.SUBTRACT)

    # LPattern1 copy 8 sketch → LPattern1 copy 8 (revolve, cut)
    with BuildSketch(Plane(origin=(157.403183332, -6.846378111, 20), x_dir=(0, 0, 1), z_dir=(1, 0, 0))):
        Polygon((0, 0), (0, 15.2618073), (2.1, 14), (2.1, 0), align=None)
    revolve(axis=Axis((157.403183332, -0.496378111, 20), (0, -1, 0)), mode=Mode.SUBTRACT)

    # LPattern1 copy 9 sketch → LPattern1 copy 9 (revolve, cut)
    with BuildSketch(Plane(origin=(19.4, -6.846378111, -10), x_dir=(0, 0, 1), z_dir=(1, 0, 0))):
        Polygon((0, 0), (0, 15.2618073), (2.1, 14), (2.1, 0), align=None)
    revolve(axis=Axis((19.4, -0.496378111, -10), (0, -1, 0)), mode=Mode.SUBTRACT)

    # LPattern1 copy 10 sketch → LPattern1 copy 10 (revolve, cut)
    with BuildSketch(Plane(origin=(-10.6, -6.846378111, -10), x_dir=(0, 0, 1), z_dir=(1, 0, 0))):
        Polygon((0, 0), (0, 15.2618073), (2.1, 14), (2.1, 0), align=None)
    revolve(axis=Axis((-10.6, -0.496378111, -10), (0, -1, 0)), mode=Mode.SUBTRACT)

    # LPattern1 copy 11 sketch → LPattern1 copy 11 (revolve, cut)
    with BuildSketch(Plane(origin=(127.4, -6.846378111, -10), x_dir=(0, 0, 1), z_dir=(1, 0, 0))):
        Polygon((0, 0), (0, 15.2618073), (2.1, 14), (2.1, 0), align=None)
    revolve(axis=Axis((127.4, -0.496378111, -10), (0, -1, 0)), mode=Mode.SUBTRACT)

    # LPattern1 copy 12 sketch → LPattern1 copy 12 (revolve, cut)
    with BuildSketch(Plane(origin=(157.4, -6.846378111, -10), x_dir=(0, 0, 1), z_dir=(1, 0, 0))):
        Polygon((0, 0), (0, 15.2618073), (2.1, 14), (2.1, 0), align=None)
    revolve(axis=Axis((157.4, -0.496378111, -10), (0, -1, 0)), mode=Mode.SUBTRACT)

    # LPattern1 copy 13 sketch → LPattern1 copy 13 (revolve, cut)
    with BuildSketch(Plane(origin=(157.4, -6.846378111, 10), x_dir=(0, 0, 1), z_dir=(1, 0, 0))):
        Polygon((0, 0), (0, 15.2618073), (2.1, 14), (2.1, 0), align=None)
    revolve(axis=Axis((157.4, -0.496378111, 10), (0, -1, 0)), mode=Mode.SUBTRACT)

    # LPattern1 copy 14 sketch → LPattern1 copy 14 (revolve, cut)
    with BuildSketch(Plane(origin=(127.4, -6.846378111, 10), x_dir=(0, 0, 1), z_dir=(1, 0, 0))):
        Polygon((0, 0), (0, 15.2618073), (2.1, 14), (2.1, 0), align=None)
    revolve(axis=Axis((127.4, -0.496378111, 10), (0, -1, 0)), mode=Mode.SUBTRACT)

    # LPattern1 copy 15 sketch → LPattern1 copy 15 (revolve, cut)
    with BuildSketch(Plane(origin=(19.4, -6.846378111, 10), x_dir=(0, 0, 1), z_dir=(1, 0, 0))):
        Polygon((0, 0), (0, 15.2618073), (2.1, 14), (2.1, 0), align=None)
    revolve(axis=Axis((19.4, -0.496378111, 10), (0, -1, 0)), mode=Mode.SUBTRACT)


solid = part.part
